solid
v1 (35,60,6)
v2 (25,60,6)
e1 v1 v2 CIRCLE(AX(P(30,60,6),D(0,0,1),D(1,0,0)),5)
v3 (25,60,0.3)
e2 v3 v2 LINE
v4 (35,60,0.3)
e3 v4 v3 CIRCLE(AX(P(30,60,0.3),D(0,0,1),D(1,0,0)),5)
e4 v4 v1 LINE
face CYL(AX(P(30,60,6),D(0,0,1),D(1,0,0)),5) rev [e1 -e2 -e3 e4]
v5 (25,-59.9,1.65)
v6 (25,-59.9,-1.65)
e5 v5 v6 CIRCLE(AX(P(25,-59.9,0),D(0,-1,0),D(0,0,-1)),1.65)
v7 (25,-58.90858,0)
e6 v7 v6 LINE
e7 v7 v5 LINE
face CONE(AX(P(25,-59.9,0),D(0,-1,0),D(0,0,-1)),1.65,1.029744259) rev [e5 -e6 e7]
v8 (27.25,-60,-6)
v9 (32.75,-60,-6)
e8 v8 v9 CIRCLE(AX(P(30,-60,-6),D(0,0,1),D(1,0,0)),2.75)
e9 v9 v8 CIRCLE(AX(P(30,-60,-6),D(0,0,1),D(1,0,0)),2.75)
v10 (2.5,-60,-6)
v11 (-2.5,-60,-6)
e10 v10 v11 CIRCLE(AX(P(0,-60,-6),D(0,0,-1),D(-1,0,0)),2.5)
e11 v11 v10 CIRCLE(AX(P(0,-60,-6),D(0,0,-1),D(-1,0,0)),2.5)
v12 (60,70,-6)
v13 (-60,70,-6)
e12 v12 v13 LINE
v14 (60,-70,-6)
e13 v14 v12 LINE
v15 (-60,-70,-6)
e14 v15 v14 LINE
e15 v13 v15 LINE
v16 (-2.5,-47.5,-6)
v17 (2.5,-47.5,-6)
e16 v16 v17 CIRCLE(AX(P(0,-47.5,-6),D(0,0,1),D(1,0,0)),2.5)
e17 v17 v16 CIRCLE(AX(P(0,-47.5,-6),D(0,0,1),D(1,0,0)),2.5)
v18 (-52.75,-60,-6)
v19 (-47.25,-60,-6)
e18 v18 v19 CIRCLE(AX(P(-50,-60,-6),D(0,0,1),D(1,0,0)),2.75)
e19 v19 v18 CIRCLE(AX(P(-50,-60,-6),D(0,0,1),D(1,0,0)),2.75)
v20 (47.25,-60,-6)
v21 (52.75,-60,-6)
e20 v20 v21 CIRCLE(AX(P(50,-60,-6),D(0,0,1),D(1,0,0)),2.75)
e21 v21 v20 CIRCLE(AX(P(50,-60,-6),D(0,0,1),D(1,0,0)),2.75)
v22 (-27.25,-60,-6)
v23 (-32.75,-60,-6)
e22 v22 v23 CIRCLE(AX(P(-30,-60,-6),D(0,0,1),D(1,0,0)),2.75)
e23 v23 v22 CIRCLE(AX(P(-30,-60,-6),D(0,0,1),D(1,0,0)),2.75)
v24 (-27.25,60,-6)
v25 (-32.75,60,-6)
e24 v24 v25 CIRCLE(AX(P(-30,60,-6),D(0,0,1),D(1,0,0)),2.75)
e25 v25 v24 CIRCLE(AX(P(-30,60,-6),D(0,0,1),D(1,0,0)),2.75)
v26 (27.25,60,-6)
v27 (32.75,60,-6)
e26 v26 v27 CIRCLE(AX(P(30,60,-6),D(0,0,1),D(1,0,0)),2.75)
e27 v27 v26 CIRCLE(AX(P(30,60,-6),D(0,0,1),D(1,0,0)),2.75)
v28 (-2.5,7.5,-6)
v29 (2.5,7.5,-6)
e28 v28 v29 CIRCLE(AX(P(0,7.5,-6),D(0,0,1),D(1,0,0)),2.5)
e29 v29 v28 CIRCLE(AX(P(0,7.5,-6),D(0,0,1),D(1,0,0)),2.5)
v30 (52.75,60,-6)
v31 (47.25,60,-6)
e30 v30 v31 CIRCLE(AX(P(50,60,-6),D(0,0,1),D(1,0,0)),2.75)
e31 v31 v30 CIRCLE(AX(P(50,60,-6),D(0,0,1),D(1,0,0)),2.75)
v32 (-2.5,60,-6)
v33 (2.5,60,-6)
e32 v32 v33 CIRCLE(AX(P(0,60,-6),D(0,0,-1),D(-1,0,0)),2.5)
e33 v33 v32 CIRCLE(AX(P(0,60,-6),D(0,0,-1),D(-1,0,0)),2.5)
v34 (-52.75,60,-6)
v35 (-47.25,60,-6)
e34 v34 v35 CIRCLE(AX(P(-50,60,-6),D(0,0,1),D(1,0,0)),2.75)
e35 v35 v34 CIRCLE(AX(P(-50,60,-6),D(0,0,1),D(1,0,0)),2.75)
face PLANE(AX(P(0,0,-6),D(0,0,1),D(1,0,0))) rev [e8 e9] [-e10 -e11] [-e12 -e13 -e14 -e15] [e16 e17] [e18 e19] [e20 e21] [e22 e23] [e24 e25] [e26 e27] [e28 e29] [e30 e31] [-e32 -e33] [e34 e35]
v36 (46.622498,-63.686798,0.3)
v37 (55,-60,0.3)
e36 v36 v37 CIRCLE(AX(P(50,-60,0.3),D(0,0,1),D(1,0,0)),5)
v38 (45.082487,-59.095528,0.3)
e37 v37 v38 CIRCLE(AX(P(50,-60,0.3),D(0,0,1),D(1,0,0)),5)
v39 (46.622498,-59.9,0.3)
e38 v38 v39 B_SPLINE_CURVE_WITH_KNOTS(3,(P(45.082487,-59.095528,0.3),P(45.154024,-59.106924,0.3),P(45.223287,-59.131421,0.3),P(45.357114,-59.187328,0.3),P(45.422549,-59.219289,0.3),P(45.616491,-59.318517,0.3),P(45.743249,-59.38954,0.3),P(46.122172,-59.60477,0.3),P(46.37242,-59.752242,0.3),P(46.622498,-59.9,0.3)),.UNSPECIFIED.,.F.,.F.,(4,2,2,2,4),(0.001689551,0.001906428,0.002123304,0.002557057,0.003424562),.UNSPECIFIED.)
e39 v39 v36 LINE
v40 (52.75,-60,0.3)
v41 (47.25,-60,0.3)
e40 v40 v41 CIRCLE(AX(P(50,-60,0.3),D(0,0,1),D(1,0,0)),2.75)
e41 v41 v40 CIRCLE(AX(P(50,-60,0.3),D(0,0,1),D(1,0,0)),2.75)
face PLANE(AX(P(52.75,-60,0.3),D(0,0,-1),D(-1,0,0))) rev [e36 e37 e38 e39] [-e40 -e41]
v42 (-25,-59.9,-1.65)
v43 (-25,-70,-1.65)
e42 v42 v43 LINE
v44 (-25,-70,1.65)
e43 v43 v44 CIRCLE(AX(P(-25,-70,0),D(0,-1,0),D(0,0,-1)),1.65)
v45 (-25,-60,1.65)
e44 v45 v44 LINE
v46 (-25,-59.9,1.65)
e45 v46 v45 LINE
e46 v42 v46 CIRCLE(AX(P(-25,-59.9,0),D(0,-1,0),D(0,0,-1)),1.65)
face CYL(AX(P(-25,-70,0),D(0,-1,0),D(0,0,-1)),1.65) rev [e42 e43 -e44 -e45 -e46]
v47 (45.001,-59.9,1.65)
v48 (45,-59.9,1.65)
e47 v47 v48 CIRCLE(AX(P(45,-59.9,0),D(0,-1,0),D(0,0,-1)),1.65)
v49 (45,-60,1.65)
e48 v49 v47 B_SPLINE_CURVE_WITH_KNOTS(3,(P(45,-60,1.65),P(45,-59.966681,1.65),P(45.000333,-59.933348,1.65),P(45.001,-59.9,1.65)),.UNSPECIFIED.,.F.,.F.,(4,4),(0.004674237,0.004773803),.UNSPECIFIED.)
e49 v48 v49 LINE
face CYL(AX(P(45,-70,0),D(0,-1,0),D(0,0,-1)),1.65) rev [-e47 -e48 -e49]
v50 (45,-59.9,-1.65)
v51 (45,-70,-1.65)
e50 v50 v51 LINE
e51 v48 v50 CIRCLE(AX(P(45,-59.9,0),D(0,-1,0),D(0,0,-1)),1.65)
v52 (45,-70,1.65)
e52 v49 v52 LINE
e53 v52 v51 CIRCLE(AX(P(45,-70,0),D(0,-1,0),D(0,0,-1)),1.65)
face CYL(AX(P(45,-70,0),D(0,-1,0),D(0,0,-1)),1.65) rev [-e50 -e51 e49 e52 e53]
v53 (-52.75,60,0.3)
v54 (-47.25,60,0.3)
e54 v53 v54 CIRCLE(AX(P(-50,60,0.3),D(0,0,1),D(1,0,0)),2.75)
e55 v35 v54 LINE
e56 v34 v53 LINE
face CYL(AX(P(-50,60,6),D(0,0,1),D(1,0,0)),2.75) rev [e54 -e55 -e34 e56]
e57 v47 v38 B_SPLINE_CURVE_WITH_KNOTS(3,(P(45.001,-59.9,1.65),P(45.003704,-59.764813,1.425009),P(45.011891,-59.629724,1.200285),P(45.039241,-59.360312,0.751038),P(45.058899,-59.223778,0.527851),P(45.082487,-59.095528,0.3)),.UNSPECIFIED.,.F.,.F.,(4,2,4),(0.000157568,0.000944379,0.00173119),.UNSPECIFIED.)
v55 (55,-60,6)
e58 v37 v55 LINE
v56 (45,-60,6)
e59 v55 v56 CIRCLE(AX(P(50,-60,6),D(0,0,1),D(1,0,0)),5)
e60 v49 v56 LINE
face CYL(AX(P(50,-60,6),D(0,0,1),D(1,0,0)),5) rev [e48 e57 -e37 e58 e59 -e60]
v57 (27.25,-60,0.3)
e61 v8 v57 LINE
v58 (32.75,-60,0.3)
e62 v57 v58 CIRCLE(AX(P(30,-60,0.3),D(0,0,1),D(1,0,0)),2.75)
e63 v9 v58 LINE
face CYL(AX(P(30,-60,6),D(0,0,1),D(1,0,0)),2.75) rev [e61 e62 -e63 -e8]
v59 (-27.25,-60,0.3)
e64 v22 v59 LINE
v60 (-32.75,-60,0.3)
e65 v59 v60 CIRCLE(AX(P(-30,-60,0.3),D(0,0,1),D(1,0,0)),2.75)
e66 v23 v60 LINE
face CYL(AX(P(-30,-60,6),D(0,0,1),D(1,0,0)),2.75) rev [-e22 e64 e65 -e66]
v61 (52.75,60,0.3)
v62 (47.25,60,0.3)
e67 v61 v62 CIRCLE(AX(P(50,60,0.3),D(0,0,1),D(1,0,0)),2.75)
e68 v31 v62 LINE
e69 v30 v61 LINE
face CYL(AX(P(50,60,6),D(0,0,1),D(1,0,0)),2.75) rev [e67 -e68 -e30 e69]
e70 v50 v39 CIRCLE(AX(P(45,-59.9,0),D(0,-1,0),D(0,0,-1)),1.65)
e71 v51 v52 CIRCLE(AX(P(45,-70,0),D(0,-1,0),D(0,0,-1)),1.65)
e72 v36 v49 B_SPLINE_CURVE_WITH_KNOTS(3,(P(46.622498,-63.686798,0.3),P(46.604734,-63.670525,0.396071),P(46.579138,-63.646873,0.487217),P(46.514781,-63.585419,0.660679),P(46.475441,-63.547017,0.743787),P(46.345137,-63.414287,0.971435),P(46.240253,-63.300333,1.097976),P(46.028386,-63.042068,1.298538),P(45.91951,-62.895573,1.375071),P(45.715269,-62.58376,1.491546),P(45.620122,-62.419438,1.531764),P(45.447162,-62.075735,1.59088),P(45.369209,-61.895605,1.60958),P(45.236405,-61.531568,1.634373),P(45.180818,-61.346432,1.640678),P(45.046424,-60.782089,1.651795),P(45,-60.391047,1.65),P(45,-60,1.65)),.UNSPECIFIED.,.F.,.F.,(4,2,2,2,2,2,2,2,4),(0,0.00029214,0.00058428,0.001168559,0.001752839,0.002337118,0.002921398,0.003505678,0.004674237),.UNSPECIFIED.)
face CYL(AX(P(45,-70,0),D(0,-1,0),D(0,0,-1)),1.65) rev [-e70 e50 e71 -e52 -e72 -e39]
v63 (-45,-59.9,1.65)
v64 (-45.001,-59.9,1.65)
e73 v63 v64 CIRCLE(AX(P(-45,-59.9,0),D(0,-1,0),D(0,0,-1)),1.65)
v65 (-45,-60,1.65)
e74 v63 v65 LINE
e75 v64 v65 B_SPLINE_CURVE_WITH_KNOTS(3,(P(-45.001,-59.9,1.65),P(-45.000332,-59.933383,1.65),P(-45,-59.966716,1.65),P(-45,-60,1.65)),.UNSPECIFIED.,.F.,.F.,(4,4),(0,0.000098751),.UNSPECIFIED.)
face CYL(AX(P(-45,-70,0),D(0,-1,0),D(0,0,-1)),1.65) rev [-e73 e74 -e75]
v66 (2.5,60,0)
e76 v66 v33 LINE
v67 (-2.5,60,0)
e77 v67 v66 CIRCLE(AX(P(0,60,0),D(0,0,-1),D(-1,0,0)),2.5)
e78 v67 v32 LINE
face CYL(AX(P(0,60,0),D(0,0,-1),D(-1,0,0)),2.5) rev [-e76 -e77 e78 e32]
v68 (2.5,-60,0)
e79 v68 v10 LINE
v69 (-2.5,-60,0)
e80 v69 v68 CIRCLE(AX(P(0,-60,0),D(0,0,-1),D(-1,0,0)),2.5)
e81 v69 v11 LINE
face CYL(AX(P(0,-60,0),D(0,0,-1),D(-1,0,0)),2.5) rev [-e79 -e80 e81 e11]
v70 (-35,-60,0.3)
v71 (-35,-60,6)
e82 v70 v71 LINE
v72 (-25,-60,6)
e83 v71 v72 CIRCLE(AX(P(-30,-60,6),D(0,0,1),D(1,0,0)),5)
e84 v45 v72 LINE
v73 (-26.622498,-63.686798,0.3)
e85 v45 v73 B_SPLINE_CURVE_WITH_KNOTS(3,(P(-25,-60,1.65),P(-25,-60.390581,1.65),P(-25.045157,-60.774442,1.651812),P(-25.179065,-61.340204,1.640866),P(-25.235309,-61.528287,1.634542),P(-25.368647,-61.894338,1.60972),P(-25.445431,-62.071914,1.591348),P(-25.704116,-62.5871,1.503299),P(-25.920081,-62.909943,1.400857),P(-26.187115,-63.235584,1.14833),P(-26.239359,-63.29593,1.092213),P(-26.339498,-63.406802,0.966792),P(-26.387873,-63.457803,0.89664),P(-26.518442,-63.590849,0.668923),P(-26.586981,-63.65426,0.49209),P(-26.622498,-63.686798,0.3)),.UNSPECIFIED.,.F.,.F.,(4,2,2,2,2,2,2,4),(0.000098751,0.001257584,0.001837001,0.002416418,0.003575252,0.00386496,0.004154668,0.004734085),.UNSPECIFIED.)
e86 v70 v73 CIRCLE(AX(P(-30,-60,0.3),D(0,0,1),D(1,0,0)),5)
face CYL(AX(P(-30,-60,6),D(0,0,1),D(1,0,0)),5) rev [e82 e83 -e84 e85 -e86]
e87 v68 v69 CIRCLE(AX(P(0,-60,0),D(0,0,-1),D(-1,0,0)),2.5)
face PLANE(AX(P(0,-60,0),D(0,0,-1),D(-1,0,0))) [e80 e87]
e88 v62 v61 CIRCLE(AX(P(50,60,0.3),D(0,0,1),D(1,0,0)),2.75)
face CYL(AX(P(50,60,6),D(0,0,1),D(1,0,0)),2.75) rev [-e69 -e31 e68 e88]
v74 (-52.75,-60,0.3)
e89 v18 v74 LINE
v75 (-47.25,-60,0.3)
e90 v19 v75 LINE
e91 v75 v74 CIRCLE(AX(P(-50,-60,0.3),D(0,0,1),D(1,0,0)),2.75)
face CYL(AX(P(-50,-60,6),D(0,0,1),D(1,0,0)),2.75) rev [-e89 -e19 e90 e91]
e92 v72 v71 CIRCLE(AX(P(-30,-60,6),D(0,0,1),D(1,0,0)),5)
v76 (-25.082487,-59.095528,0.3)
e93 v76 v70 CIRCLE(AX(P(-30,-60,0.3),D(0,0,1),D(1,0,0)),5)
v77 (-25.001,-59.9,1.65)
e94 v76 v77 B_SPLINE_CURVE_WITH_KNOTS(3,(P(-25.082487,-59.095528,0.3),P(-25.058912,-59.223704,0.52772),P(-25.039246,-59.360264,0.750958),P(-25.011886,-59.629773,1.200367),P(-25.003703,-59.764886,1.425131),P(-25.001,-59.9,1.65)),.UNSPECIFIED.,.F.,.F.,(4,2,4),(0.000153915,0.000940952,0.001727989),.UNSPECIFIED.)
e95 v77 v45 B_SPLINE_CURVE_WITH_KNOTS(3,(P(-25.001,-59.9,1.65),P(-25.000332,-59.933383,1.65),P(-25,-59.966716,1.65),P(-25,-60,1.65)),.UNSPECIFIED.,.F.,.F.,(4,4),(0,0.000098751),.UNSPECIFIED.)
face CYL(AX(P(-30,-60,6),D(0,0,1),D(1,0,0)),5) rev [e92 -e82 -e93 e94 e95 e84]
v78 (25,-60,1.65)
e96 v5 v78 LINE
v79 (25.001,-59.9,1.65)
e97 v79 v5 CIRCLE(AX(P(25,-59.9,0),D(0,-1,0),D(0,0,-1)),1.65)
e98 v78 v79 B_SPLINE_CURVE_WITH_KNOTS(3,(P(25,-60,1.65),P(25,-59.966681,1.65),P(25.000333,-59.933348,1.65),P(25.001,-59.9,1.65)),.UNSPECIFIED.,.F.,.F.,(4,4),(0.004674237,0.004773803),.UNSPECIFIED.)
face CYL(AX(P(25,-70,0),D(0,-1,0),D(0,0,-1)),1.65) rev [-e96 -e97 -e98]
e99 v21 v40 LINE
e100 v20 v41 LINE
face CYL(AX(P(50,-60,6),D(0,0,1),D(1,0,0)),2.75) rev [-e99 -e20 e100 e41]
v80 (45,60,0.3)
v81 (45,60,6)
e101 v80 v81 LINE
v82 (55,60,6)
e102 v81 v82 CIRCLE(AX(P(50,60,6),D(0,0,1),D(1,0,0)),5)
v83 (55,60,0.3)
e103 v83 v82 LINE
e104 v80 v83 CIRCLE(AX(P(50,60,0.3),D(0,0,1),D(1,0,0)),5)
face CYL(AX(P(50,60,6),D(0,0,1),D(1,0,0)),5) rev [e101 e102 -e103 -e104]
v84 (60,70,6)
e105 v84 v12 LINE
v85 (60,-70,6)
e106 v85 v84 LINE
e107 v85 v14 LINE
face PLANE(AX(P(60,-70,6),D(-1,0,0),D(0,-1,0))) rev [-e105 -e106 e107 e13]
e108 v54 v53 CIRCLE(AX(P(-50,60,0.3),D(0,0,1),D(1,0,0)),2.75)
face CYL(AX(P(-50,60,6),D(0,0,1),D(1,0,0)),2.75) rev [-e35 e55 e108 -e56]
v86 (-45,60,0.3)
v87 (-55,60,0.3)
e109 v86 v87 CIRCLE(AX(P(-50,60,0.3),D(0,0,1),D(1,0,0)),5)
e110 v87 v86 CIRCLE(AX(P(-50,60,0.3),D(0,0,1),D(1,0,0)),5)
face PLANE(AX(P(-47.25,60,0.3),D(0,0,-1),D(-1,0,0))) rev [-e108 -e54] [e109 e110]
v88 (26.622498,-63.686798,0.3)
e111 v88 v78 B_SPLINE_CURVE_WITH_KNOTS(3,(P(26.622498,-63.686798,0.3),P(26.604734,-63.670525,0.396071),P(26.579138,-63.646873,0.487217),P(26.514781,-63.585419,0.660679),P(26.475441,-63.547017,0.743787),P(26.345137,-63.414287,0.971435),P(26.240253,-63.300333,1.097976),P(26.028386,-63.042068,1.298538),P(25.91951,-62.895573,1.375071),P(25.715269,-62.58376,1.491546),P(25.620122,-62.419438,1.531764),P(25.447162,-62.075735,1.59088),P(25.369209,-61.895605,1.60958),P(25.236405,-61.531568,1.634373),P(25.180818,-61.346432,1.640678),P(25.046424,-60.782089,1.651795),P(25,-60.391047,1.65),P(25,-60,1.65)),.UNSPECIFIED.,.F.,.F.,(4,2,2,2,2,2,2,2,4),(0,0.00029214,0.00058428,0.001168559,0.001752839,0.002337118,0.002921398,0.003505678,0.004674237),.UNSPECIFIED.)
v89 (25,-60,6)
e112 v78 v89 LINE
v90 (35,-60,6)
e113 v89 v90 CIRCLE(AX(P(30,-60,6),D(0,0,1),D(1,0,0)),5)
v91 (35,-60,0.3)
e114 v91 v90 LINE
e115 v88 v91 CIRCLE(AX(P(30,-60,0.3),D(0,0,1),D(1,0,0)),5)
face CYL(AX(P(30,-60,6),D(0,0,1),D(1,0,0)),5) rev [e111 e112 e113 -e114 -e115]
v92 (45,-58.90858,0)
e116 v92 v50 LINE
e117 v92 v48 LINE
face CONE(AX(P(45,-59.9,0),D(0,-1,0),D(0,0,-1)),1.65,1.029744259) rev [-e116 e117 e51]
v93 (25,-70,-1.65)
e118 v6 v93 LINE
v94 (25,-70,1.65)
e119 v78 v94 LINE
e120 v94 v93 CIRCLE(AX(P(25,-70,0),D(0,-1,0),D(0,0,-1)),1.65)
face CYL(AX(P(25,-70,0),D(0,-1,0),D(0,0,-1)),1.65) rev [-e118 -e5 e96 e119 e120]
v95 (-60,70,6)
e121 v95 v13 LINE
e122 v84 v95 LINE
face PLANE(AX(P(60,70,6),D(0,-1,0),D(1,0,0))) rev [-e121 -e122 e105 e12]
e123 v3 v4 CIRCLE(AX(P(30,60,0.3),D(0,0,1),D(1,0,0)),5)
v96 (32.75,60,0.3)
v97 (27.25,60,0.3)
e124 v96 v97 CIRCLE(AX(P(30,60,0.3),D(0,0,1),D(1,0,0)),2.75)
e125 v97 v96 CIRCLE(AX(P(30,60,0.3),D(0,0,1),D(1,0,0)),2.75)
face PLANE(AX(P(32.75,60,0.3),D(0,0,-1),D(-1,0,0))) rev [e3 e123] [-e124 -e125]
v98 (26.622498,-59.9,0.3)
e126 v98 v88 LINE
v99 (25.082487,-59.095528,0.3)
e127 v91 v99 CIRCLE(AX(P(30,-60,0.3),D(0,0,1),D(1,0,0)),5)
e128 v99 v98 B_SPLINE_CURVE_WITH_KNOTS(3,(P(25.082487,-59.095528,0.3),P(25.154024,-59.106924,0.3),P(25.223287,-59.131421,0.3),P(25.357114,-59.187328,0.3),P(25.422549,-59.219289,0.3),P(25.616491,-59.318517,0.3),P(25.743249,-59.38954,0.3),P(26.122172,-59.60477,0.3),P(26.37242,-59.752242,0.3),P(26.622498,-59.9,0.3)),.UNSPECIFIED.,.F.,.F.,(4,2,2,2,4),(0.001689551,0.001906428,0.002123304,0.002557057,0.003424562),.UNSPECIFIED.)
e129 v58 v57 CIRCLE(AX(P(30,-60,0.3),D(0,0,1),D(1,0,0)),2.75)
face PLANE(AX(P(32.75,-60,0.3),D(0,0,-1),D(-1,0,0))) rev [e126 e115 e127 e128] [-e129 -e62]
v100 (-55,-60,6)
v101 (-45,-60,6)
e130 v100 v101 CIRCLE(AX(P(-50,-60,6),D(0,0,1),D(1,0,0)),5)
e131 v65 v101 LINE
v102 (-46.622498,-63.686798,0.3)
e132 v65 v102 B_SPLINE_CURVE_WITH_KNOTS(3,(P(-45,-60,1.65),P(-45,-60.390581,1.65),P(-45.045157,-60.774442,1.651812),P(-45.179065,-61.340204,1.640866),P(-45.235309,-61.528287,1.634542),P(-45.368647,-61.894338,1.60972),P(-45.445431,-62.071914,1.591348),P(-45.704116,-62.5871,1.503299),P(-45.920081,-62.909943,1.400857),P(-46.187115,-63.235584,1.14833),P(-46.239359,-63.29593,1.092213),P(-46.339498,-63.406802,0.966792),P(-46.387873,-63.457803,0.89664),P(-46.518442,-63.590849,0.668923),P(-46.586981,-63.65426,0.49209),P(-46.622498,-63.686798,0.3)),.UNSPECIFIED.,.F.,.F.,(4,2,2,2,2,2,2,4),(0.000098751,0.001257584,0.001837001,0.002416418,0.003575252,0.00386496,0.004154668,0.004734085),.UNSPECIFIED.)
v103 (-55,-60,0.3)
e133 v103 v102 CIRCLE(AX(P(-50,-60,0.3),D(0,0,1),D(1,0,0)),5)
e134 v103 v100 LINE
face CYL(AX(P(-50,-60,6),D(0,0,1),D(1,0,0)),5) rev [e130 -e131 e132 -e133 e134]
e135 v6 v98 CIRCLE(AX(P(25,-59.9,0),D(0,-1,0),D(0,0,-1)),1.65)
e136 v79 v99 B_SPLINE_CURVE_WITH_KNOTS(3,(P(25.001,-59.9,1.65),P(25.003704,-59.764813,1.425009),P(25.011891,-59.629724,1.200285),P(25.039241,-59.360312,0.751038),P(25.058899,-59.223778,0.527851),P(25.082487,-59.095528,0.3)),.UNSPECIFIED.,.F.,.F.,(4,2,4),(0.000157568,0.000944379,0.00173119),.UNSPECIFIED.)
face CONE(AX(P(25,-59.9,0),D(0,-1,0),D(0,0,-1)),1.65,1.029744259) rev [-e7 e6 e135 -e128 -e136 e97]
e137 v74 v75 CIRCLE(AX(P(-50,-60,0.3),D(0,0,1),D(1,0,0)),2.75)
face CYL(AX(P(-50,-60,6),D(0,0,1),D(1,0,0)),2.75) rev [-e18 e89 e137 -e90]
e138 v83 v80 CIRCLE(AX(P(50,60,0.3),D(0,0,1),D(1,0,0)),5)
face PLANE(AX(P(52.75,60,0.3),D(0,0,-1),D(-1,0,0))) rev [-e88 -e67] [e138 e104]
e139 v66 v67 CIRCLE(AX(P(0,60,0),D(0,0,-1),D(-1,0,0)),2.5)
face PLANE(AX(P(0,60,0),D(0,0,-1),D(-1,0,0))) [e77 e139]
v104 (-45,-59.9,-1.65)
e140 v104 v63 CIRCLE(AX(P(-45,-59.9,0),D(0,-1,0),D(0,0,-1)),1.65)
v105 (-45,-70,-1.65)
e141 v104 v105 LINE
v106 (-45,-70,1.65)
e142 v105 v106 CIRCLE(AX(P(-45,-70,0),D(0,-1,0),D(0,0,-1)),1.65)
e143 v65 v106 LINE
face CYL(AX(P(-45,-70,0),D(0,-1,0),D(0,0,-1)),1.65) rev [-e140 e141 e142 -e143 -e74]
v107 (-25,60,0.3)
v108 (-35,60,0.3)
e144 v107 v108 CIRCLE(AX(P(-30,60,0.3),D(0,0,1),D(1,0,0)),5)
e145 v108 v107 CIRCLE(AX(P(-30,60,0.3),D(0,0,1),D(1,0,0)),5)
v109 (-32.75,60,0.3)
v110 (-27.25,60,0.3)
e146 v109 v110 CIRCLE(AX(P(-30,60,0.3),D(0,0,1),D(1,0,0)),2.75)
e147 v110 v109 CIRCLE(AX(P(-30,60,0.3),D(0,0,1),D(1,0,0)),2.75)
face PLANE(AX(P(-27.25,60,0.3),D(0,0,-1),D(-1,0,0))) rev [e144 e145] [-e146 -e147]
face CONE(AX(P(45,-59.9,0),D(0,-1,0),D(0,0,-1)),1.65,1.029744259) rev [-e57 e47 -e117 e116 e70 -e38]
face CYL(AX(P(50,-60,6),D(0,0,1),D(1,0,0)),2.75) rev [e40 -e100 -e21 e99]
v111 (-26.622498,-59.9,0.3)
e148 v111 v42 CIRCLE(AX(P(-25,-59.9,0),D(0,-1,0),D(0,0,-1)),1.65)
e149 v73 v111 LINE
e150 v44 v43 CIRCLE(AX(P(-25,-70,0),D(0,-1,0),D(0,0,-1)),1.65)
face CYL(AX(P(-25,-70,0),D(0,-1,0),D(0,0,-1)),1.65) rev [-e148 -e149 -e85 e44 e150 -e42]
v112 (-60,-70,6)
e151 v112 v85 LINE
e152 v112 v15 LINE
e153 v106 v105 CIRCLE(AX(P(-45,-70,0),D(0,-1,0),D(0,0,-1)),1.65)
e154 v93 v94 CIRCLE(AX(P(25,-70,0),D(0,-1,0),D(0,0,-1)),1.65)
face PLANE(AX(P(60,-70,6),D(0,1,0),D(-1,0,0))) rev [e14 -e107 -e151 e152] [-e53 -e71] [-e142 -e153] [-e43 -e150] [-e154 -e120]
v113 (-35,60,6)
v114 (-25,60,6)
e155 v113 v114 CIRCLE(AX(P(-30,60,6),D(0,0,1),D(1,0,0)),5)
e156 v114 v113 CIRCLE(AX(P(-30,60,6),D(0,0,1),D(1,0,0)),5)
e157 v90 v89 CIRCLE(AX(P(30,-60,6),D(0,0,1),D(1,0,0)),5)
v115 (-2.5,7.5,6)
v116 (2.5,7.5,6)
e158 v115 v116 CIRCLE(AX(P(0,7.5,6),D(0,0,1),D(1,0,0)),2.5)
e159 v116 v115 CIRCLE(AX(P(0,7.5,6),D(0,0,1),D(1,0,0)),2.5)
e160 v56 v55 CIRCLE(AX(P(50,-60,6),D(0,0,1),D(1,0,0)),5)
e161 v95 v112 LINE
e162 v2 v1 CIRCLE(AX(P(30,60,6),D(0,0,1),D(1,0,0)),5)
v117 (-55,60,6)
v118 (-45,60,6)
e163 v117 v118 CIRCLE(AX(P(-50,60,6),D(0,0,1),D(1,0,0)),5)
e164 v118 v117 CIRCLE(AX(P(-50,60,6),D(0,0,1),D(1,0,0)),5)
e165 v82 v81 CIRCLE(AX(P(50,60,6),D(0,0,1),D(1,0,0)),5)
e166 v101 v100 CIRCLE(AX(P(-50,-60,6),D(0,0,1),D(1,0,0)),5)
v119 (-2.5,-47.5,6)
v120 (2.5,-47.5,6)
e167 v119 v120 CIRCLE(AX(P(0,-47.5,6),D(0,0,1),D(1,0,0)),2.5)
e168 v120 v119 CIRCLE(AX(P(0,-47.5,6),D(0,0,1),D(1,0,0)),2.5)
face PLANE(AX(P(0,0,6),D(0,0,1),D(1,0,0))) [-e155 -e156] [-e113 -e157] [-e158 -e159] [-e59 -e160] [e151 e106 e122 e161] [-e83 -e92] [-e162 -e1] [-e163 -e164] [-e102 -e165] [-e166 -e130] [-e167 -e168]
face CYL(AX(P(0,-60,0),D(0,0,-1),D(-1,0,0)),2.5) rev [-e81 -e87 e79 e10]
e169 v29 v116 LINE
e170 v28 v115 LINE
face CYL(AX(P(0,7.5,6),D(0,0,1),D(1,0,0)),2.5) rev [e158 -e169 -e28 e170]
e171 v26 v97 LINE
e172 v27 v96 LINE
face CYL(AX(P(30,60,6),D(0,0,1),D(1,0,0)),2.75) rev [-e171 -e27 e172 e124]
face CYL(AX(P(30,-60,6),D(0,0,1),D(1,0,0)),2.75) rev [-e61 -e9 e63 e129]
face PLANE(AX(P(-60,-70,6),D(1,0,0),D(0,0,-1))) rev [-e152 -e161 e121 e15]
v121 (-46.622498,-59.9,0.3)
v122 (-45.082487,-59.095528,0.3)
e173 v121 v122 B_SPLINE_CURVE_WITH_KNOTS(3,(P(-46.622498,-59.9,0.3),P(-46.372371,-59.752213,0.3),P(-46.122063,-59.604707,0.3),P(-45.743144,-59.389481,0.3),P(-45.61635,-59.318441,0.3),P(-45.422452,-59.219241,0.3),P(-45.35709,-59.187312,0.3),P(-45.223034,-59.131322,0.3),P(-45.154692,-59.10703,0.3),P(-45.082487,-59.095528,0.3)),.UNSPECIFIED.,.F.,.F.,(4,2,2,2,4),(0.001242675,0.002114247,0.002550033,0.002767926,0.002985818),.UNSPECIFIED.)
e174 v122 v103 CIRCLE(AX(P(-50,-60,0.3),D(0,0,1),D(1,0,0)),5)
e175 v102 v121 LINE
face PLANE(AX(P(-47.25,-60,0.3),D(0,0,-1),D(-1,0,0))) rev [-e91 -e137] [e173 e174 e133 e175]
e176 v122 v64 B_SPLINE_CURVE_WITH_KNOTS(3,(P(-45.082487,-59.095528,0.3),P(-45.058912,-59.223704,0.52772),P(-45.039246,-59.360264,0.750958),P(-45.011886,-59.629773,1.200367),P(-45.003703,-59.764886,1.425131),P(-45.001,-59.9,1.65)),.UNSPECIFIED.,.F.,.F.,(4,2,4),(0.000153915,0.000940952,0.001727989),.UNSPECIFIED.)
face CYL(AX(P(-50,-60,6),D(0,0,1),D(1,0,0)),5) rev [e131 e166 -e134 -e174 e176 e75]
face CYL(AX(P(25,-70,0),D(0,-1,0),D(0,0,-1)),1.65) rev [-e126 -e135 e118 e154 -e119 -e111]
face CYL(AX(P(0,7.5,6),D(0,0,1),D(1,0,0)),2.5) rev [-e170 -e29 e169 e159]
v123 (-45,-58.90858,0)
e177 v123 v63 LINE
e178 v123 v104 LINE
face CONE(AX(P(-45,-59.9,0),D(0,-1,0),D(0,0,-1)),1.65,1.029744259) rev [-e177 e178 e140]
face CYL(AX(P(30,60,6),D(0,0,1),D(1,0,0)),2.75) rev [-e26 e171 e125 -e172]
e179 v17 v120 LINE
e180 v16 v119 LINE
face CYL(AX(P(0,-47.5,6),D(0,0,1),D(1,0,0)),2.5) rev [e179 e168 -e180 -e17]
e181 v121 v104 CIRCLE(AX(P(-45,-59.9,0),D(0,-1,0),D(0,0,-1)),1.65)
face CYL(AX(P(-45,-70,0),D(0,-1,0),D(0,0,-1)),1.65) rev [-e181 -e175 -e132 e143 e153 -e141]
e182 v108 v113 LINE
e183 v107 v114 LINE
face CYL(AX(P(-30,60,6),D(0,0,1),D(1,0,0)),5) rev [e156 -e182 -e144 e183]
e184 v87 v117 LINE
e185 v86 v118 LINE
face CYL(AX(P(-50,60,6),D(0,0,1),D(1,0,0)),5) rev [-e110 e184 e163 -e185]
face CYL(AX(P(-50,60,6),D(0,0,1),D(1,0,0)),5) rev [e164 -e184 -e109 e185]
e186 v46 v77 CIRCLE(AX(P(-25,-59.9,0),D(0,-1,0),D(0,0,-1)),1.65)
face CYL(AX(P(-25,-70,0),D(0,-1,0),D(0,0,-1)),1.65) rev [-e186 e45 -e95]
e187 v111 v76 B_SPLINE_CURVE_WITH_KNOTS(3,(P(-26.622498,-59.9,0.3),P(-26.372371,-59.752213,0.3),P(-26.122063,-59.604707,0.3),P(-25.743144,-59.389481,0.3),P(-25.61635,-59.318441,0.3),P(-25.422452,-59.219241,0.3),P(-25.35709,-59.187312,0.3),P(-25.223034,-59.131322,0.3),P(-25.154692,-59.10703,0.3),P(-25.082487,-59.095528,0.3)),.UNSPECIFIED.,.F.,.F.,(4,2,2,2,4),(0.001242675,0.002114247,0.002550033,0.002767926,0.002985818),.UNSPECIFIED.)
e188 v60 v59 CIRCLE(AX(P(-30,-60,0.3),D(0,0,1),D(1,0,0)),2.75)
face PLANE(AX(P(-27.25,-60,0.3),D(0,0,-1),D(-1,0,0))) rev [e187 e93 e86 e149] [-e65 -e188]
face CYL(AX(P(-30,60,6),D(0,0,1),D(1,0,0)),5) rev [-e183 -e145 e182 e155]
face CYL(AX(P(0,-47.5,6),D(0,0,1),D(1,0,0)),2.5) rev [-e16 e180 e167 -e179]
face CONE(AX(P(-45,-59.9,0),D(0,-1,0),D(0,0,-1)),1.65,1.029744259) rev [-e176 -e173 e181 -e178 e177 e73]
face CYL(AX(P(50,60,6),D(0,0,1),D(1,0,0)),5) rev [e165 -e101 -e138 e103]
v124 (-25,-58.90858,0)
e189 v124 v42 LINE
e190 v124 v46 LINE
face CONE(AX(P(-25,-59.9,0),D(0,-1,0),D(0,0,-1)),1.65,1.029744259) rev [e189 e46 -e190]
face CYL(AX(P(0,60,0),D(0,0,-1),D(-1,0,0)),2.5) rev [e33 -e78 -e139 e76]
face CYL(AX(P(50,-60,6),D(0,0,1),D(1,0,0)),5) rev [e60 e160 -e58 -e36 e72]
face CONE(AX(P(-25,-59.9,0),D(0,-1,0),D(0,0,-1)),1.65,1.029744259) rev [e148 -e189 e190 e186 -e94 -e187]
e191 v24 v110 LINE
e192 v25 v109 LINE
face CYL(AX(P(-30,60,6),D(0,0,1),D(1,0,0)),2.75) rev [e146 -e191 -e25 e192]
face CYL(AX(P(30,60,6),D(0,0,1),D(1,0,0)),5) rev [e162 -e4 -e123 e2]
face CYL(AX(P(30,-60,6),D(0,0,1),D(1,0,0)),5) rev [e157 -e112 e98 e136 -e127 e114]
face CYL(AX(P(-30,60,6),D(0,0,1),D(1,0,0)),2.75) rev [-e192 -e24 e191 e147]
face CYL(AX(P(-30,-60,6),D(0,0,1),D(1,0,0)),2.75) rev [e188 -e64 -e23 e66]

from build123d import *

# Parameters (mm, degrees)
SKETCH_1_W                  = 120
SKETCH_1_H                  = 140
EXTRUDE_1_DEPTH             = 6
HOLE_WIZARD_M6_1_D          = 5
HOLE_WIZARD_M6_1_DEPTH      = 15
HOLE_WIZARD_M6_1_TIP        = 1.502151548
HOLE_WIZARD_1_D             = 5.5
HOLE_WIZARD_1_DEPTH         = 15
HOLE_WIZARD_1_CBORE_D       = 10
HOLE_WIZARD_1_CBORE_DEPTH   = 5.7
HOLE_WIZARD_1_TIP           = 1.652366702
SKETCH_5_R                  = 2.5
CUT_EXTRUDE_1_DEPTH         = 6
HOLE_WIZARD_M4_2_AT_2_COUNT = 2
HOLE_WIZARD_M4_2_AT_2_PITCH = 20


with BuildPart() as part:
    # 草图1 → 凸台-拉伸1 (new, symmetric)
    with BuildSketch(Plane.XY):
        Rectangle(SKETCH_1_W, SKETCH_1_H)
    extrude(amount=EXTRUDE_1_DEPTH, both=True)

    # M6 螺纹孔1
    with Locations(Plane(origin=(0, -47.5, 6), x_dir=(1, 0, 0), z_dir=(0, 0, 1))):
        with Locations((0, 0), (0, 55)):
            Hole(HOLE_WIZARD_M6_1_D / 2, depth=HOLE_WIZARD_M6_1_DEPTH)
            with Locations((0, 0, -(HOLE_WIZARD_M6_1_DEPTH + HOLE_WIZARD_M6_1_TIP / 2))):  # 118° drill point
                Cone(0, HOLE_WIZARD_M6_1_D / 2, HOLE_WIZARD_M6_1_TIP, mode=Mode.SUBTRACT)

    # 打孔尺寸(%根据)内六角圆柱头螺钉的类型1
    with Locations(Plane(origin=(-50, 60, 6), x_dir=(1, 0, 0), z_dir=(0, 0, 1))):
        with Locations((0, 0), (20, 0), (80, 0), (100, 0), (100, -120), (80, -120), (20, -120), (0, -120)):
            CounterBoreHole(HOLE_WIZARD_1_D / 2, HOLE_WIZARD_1_CBORE_D / 2, HOLE_WIZARD_1_CBORE_DEPTH, depth=HOLE_WIZARD_1_DEPTH)
            with Locations((0, 0, -(HOLE_WIZARD_1_DEPTH + HOLE_WIZARD_1_TIP / 2))):  # 118° drill point
                Cone(0, HOLE_WIZARD_1_D / 2, HOLE_WIZARD_1_TIP, mode=Mode.SUBTRACT)

    # 草图5 → 切除-拉伸1 (cut)
    with BuildSketch(Plane(origin=(0, 0, -6), x_dir=(-1, 0, 0), z_dir=(0, 0, -1))):
        with Locations((0, 60)):
            Circle(SKETCH_5_R)
        with Locations((0, -60)):
            Circle(SKETCH_5_R)
    extrude(amount=-CUT_EXTRUDE_1_DEPTH, mode=Mode.SUBTRACT)

    # 草图11 → M4 螺纹孔2 (revolve, cut)
    with BuildSketch(Plane(origin=(25, -70, 0), x_dir=(0, 0, -1), z_dir=(1, 0, 0))):
        Polygon((0, 0), (0, 11.091420021), (1.65, 10.1), (1.65, 0), align=None)
    hole_wizard_m4_2 = revolve(axis=Axis((25, -76.35, 0), (0, 1, 0)), mode=Mode.SUBTRACT)

    # M4 螺纹孔2 at 2: M4 螺纹孔2 ×2
    with Locations(*[(i * HOLE_WIZARD_M4_2_AT_2_PITCH, 0, 0) for i in range(1, HOLE_WIZARD_M4_2_AT_2_COUNT)]):
        add(hole_wizard_m4_2, mode=Mode.SUBTRACT)

    # 镜向1: M4 螺纹孔2 across plane
    add(hole_wizard_m4_2.mirror(Plane(origin=(0, 0, 0), x_dir=(0, 0, 1), z_dir=(1, 0, 0))), mode=Mode.SUBTRACT)

    # 镜向1 copy 1 sketch → 镜向1 copy 1 (revolve, cut)
    with BuildSketch(Plane(origin=(-45, -70, 0), x_dir=(0, 0, -1), z_dir=(-1, 0, 0))):
        Polygon((0, 0), (0, -11.091420021), (1.65, -10.1), (1.65, 0), align=None)
    revolve(axis=Axis((-45, -76.35, 0), (0, -1, 0)), mode=Mode.SUBTRACT)


solid = part.part
